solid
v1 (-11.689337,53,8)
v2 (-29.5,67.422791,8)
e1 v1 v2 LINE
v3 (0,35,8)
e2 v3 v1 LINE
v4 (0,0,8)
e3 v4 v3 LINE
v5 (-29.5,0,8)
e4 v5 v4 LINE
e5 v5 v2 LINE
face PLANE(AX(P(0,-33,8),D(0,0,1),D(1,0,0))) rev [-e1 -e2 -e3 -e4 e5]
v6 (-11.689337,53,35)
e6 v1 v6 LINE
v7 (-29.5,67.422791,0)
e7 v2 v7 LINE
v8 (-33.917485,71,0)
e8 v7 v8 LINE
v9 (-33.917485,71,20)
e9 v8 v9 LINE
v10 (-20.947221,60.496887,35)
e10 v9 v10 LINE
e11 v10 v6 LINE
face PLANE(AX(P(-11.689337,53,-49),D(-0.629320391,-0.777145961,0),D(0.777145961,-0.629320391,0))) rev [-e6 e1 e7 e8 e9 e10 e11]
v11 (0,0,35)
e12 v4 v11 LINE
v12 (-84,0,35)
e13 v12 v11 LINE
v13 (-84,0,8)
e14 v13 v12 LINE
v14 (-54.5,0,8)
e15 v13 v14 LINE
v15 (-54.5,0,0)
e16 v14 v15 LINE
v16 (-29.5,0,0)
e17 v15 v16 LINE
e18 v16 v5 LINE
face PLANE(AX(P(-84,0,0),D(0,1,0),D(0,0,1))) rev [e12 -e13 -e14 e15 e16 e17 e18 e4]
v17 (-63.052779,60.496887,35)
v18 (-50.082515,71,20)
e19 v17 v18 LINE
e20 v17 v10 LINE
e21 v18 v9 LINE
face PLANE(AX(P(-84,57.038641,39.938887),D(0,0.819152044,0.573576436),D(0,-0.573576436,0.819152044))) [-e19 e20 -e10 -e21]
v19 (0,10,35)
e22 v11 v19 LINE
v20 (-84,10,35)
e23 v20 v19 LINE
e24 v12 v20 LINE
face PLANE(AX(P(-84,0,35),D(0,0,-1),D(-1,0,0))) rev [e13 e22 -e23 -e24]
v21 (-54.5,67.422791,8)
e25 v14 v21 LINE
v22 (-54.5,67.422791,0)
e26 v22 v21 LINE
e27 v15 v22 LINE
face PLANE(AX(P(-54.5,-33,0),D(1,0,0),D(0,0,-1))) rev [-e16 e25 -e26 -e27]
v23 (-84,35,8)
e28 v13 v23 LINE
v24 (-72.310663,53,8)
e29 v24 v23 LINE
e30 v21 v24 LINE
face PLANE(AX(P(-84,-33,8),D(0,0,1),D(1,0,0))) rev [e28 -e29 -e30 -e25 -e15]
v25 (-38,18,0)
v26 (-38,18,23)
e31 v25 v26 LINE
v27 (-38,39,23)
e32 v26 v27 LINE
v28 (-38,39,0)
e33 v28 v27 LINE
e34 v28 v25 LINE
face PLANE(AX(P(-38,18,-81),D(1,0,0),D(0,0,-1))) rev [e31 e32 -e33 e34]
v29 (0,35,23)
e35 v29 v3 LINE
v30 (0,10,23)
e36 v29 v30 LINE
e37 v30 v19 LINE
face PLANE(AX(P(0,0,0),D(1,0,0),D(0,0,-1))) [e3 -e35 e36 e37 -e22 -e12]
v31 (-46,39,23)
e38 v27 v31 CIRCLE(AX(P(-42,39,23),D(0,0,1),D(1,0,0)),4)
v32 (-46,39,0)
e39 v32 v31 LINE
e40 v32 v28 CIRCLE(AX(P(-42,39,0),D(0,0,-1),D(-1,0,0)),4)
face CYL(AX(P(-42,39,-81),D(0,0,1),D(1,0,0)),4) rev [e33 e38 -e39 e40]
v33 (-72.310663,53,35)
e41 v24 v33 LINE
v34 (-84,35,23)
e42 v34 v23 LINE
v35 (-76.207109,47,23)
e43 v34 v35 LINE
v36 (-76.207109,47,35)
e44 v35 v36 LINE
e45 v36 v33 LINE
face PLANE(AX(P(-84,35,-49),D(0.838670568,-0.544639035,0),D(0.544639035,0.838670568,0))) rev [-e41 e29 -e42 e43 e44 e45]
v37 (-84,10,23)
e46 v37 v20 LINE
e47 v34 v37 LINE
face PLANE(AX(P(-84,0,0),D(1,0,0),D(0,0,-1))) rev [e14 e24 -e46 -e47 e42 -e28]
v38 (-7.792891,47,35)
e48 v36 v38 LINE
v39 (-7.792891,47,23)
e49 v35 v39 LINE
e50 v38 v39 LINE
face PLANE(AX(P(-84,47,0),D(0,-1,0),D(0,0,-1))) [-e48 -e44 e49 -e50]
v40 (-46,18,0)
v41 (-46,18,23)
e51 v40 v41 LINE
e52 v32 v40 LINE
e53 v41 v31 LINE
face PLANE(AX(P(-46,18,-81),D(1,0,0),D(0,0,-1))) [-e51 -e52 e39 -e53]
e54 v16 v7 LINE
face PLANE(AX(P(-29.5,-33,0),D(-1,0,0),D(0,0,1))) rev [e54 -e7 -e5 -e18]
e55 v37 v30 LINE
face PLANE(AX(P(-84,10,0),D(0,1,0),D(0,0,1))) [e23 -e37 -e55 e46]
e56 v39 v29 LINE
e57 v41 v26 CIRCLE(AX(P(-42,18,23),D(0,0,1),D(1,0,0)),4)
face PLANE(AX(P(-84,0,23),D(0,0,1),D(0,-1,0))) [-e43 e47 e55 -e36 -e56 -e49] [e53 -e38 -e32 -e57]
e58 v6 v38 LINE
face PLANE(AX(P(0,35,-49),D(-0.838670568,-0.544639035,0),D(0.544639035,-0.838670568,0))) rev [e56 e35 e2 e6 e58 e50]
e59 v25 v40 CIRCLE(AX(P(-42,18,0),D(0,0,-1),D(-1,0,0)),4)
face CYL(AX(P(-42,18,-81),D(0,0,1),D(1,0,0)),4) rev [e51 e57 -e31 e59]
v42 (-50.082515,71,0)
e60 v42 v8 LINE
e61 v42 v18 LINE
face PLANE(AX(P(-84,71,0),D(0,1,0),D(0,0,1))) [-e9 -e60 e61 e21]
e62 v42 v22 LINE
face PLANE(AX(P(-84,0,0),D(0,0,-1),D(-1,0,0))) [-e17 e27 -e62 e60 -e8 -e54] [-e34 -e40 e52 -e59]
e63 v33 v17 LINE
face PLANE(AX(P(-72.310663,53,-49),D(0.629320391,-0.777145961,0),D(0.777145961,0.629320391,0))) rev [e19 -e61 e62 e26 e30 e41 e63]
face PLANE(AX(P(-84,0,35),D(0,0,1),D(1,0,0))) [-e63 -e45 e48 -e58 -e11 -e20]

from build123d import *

# Parameters (mm, degrees)
SUPPORT_BLOCK_84MM_DEPTH = 84
TOP_BEVEL_CUT_DEPTH      = 84
SLOT_8MM_SKETCH_W        = 29.5
SLOT_8MM_SKETCH_H        = 8
SLOT_8MM_CUT_DEPTH       = 104
SLOT_8X21_CUT_DEPTH      = 104


with BuildPart() as part:
    # Block Profile Sketch → Support Block 84mm (new body)
    with BuildSketch(Plane(origin=(0, 0, 0), x_dir=(0, 0, -1), z_dir=(1, 0, 0))):
        Polygon((-23, 47), (-23, 10), (-35, 10), (-35, 0), (0, 0), (0, 71), (-20, 71), (-35, 60.496886927), (-35, 47), align=None)
    extrude(amount=-SUPPORT_BLOCK_84MM_DEPTH)

    # Top Bevel Sketch → Top Bevel Cut (cut)
    with BuildSketch(Plane.XY.offset(35)):
        Polygon((0, 35), (-11.689336678, 53), (-33.917485495, 71), (24.610458678, 71), (24.610458678, 35), align=None)
        Polygon((-50.082514505, 71), (-95.876326583, 71), (-95.876326583, 33.772958176), (-84, 35), (-72.310663322, 53), align=None)
    extrude(amount=-TOP_BEVEL_CUT_DEPTH, mode=Mode.SUBTRACT)

    # Slot 8mm Sketch → Slot 8mm Cut (cut)
    with BuildSketch(Plane(origin=(0, 71, 0), x_dir=(1, 0, 0), z_dir=(0, 1, 0))):
        with Locations((-69.25, -4)):
            Rectangle(SLOT_8MM_SKETCH_W, SLOT_8MM_SKETCH_H)
        with Locations((-14.75, -4)):
            Rectangle(SLOT_8MM_SKETCH_W, SLOT_8MM_SKETCH_H)
    extrude(amount=-SLOT_8MM_CUT_DEPTH, mode=Mode.SUBTRACT)

    # Slot 8x21 Sketch → Slot 8x21 Cut (cut)
    with BuildSketch(Plane.XY.offset(23)):
        with BuildLine():
            Line((-46, 18), (-46, 39))
            ThreePointArc((-46, 39), (-42, 43), (-38, 39))
            Line((-38, 39), (-38, 18))
            ThreePointArc((-38, 18), (-42, 14), (-46, 18))
        make_face()
    extrude(amount=-SLOT_8X21_CUT_DEPTH, mode=Mode.SUBTRACT)


solid = part.part
